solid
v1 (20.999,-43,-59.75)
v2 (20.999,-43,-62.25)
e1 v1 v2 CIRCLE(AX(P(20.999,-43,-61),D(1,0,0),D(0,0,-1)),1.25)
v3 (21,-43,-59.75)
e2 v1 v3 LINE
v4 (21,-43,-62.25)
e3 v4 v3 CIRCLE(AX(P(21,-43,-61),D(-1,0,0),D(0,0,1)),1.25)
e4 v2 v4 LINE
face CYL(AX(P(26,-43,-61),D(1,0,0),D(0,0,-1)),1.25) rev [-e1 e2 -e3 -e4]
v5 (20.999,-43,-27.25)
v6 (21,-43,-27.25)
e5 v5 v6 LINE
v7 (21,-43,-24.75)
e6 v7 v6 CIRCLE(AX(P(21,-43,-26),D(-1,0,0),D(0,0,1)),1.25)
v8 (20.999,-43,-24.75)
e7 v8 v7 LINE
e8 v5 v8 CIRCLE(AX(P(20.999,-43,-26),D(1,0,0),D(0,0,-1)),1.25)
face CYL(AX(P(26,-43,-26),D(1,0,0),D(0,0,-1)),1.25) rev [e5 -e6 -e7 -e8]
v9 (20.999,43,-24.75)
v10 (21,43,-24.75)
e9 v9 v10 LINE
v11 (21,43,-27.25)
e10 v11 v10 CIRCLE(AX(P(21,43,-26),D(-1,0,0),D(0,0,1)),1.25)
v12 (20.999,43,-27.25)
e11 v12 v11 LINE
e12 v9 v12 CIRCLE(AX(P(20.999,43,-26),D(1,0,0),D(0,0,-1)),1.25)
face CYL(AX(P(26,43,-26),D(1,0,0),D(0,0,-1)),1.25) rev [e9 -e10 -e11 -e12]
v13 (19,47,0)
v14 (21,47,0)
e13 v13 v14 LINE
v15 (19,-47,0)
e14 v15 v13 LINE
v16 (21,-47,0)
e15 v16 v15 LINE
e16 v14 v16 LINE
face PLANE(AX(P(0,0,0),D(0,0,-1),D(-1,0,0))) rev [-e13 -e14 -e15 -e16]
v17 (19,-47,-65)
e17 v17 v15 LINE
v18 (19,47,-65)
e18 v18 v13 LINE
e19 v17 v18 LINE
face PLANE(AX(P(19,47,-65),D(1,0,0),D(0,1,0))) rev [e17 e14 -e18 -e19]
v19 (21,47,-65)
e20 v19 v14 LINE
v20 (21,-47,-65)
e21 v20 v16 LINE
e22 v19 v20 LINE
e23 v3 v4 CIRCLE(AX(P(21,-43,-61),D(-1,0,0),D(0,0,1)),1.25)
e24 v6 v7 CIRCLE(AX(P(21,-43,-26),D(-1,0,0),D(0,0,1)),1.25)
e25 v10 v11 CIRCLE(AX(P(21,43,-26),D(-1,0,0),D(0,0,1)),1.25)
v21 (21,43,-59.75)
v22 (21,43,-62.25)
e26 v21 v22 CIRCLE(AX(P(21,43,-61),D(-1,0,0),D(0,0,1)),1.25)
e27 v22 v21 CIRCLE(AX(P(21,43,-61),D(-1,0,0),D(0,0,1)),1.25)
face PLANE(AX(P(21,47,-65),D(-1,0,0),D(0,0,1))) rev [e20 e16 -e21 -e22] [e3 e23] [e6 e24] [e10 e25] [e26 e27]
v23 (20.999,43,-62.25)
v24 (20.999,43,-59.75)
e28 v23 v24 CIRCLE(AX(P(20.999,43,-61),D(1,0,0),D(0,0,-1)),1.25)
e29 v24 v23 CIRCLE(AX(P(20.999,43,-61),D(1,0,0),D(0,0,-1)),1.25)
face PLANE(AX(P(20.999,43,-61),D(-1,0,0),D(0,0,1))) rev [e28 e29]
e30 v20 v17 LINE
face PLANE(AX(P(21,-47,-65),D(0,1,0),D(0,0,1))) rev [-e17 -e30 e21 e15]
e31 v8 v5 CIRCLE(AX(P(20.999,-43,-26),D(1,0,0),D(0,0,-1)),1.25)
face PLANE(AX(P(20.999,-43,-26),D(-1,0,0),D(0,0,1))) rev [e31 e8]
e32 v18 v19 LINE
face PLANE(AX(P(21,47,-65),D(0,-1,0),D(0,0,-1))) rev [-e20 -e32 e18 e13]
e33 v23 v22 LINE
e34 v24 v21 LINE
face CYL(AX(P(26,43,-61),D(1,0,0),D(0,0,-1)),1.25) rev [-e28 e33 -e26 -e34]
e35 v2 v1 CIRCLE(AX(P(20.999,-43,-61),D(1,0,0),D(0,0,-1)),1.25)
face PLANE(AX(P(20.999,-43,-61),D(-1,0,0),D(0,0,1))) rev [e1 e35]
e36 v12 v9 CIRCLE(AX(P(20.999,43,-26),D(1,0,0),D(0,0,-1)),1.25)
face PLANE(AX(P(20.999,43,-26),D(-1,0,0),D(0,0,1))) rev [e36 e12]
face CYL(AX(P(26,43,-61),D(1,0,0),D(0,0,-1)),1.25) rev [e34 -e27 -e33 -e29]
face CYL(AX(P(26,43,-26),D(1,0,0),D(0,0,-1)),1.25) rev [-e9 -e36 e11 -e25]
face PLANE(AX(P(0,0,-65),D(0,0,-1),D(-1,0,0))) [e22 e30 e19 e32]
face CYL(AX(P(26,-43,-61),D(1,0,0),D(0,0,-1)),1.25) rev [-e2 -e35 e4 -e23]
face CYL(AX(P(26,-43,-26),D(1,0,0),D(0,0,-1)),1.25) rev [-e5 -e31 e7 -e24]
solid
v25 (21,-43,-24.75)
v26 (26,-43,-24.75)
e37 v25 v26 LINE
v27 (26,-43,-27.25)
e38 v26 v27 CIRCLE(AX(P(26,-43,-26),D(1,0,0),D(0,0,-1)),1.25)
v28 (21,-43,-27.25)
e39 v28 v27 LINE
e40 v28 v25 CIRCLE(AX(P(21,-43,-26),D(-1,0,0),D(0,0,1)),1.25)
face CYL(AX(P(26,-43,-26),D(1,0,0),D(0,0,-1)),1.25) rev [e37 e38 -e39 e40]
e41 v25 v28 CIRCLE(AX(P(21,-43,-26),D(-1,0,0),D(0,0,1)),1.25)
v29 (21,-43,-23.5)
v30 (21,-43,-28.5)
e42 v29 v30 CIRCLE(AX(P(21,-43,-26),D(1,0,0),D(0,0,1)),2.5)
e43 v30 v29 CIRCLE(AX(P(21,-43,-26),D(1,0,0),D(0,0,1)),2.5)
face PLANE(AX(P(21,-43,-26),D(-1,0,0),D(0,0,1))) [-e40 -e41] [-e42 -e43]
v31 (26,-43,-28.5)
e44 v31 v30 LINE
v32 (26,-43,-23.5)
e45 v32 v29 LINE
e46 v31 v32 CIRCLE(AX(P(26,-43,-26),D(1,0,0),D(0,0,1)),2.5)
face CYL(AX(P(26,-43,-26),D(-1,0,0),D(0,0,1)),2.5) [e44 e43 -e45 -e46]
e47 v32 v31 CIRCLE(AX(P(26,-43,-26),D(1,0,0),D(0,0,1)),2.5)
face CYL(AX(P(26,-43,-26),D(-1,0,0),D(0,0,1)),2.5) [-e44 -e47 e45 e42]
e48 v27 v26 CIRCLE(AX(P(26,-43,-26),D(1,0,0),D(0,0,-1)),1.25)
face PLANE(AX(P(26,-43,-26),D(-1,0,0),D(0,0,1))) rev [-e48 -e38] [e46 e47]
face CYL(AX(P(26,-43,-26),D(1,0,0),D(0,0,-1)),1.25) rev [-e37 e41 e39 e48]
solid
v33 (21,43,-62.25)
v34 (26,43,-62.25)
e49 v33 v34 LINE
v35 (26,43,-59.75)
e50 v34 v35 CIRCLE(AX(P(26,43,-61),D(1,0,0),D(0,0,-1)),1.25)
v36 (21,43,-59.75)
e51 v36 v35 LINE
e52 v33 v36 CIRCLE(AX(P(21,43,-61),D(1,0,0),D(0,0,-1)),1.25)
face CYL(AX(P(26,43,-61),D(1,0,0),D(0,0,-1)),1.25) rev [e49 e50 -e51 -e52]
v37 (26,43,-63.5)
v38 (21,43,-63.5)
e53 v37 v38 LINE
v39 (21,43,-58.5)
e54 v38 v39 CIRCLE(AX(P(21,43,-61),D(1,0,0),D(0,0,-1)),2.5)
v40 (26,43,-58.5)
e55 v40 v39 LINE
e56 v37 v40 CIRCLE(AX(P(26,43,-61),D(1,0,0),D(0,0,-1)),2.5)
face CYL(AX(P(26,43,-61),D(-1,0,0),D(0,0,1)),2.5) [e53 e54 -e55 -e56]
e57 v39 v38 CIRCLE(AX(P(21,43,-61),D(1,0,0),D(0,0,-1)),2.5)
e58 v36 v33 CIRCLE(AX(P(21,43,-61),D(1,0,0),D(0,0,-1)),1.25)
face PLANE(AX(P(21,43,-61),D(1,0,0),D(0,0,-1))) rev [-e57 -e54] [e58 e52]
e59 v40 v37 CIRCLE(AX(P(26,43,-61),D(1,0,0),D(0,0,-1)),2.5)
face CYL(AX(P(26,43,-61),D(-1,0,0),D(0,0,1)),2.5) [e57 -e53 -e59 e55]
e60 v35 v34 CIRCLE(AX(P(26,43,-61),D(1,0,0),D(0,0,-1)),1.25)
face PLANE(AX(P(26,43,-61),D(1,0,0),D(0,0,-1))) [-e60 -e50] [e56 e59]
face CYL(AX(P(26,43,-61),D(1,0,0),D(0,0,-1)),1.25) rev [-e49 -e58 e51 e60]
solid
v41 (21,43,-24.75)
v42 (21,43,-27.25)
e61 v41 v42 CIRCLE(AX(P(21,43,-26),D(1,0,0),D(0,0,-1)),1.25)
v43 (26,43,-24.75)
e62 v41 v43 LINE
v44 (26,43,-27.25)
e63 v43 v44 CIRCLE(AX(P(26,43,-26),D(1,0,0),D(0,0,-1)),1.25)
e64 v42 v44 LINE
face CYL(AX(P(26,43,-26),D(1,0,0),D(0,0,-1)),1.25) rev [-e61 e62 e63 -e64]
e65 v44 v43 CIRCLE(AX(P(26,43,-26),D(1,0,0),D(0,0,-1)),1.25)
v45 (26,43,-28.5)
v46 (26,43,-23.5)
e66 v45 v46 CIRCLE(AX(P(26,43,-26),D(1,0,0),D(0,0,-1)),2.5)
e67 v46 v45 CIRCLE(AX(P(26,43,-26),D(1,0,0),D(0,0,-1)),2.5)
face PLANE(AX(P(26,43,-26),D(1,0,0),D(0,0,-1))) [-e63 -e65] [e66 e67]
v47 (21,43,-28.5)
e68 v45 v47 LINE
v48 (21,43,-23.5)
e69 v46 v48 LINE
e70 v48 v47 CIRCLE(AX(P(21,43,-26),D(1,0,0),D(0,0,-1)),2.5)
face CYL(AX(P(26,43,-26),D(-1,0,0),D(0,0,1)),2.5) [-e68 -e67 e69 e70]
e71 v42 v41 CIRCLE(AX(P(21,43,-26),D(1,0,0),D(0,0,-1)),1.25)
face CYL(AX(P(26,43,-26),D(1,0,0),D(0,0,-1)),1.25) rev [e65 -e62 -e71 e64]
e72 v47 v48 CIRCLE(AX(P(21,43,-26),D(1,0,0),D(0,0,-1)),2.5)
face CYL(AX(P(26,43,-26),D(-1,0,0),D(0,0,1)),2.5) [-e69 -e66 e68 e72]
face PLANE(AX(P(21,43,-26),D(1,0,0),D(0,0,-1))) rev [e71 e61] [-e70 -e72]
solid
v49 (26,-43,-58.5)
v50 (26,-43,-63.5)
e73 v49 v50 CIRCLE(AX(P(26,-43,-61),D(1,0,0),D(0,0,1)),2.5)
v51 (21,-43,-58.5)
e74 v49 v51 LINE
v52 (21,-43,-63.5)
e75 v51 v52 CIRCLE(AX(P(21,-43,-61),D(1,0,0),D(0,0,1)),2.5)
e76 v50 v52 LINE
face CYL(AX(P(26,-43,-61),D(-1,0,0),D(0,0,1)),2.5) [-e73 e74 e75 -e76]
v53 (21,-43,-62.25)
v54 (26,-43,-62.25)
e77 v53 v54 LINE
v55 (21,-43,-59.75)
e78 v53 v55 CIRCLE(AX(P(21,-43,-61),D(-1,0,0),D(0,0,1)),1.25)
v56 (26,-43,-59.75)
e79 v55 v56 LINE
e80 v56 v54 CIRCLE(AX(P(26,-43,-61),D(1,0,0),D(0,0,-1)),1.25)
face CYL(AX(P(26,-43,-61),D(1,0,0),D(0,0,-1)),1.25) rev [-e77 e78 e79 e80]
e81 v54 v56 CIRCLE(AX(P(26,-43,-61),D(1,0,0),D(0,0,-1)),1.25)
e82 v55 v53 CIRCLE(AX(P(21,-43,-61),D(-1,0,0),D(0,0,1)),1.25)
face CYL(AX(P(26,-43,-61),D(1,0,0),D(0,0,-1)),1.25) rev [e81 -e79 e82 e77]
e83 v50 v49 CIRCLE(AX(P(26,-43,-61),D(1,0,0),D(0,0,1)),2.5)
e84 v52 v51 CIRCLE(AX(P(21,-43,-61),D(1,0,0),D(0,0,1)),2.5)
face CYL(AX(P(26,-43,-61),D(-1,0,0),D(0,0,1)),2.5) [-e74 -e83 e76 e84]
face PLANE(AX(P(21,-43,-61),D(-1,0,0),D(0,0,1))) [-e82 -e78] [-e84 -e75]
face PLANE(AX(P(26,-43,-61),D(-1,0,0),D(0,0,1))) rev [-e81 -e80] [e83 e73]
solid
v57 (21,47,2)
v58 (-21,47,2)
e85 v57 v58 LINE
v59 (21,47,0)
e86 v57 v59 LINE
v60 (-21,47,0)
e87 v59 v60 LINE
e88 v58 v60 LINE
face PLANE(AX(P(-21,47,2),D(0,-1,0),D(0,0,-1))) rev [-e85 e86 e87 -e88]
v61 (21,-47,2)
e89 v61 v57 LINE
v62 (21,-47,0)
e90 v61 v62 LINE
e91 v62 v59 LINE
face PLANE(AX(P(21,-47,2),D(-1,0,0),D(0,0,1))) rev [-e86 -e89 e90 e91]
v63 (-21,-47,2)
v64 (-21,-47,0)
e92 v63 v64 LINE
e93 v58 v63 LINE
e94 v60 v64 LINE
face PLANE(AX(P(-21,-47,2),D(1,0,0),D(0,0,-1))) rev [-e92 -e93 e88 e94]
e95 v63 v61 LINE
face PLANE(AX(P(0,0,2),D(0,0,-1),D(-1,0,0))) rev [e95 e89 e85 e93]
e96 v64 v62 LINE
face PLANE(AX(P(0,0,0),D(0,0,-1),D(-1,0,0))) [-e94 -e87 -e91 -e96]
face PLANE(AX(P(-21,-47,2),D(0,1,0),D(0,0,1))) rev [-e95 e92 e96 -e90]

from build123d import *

# Parameters (mm, degrees)
SKETCH_1_W                  = 42
SKETCH_1_H                  = 94
EXTRUDE_1_DEPTH             = 2
SKETCH_2_W                  = 2
SKETCH_2_H                  = 94
EXTRUDE_2_DEPTH             = 65
SKETCH_3_R                  = 2.5
EXTRUDE_3_DEPTH             = 5
EXTRUDE_3_2_DEPTH           = 5
EXTRUDE_3_3_DEPTH           = 5
EXTRUDE_3_4_DEPTH           = 5
SKETCH_5_W                  = 1.25
SKETCH_5_H                  = 5.001
HOLE_WIZARD_M3_1_AT_2_COUNT = 2
HOLE_WIZARD_M3_1_AT_2_PITCH = 35
HOLE_WIZARD_M3_1_AT_3_COUNT = 2
HOLE_WIZARD_M3_1_AT_3_PITCH = 86
HOLE_WIZARD_M3_1_AT_4_COUNT = 2
HOLE_WIZARD_M3_1_AT_4_PITCH = 92.849340332


with BuildPart() as part:
    # 草图1 → 凸台-拉伸1 (new body)
    with BuildSketch(Plane.XY):
        Rectangle(SKETCH_1_W, SKETCH_1_H)
    extrude(amount=EXTRUDE_1_DEPTH)


with BuildPart() as body_2:
    # 草图2 → 凸台-拉伸2 (new body)
    with BuildSketch(Plane(origin=(0, 0, 0), x_dir=(-1, 0, 0), z_dir=(0, 0, -1))):
        with Locations((-20, 0)):
            Rectangle(SKETCH_2_W, SKETCH_2_H)
    extrude(amount=EXTRUDE_2_DEPTH)


with BuildPart() as body_3:
    # 草图3 → 凸台-拉伸3 (new body)
    with BuildSketch(Plane(origin=(21, 0, 0), x_dir=(0, 0, -1), z_dir=(1, 0, 0))):
        with Locations((26, 43)):
            Circle(SKETCH_3_R)
    extrude(amount=EXTRUDE_3_DEPTH)


with BuildPart() as body_4:
    # 草图3 → Extrude 3 2 (new body)
    with BuildSketch(Plane(origin=(21, 0, 0), x_dir=(0, 0, -1), z_dir=(1, 0, 0))):
        with Locations((61, 43)):
            Circle(SKETCH_3_R)
    extrude(amount=EXTRUDE_3_2_DEPTH)


with BuildPart() as body_5:
    # 草图3 → Extrude 3 3 (new body)
    with BuildSketch(Plane(origin=(21, 0, 0), x_dir=(0, 0, -1), z_dir=(1, 0, 0))):
        with Locations(Location((61, -43, 0), (0, 0, 180))):
            Circle(SKETCH_3_R)
    extrude(amount=EXTRUDE_3_3_DEPTH)


with BuildPart() as body_6:
    # 草图3 → Extrude 3 4 (new body)
    with BuildSketch(Plane(origin=(21, 0, 0), x_dir=(0, 0, -1), z_dir=(1, 0, 0))):
        with Locations(Location((26, -43, 0), (0, 0, 180))):
            Circle(SKETCH_3_R)
    extrude(amount=EXTRUDE_3_4_DEPTH)


with BuildPart() as hole_wizard_m3_1_tool:
    # 草图5 → M3 螺纹孔1 (revolve)
    with BuildSketch(Plane(origin=(26, 43, -26), x_dir=(0, 0, -1), z_dir=(0, 1, 0))):
        with Locations((0.625, 2.5005)):
            Rectangle(SKETCH_5_W, SKETCH_5_H)
    hole_wizard_m3_1 = revolve(axis=Axis((32.35, 43, -26), (-1, 0, 0)))


with BuildPart() as body_2_1:
    add(body_2.part)

    # M3 螺纹孔1: cut by hole_wizard_m3_1_tool
    add(hole_wizard_m3_1_tool.part, mode=Mode.SUBTRACT)


with BuildPart() as body_3_1:
    add(body_3.part)

    # M3 螺纹孔1: cut by hole_wizard_m3_1_tool
    add(hole_wizard_m3_1_tool.part, mode=Mode.SUBTRACT)


with BuildPart() as hole_wizard_m3_1_at_2_tool:
    # M3 螺纹孔1 at 2: M3 螺纹孔1 ×2
    with Locations(*[(0, 0, -i * HOLE_WIZARD_M3_1_AT_2_PITCH) for i in range(1, HOLE_WIZARD_M3_1_AT_2_COUNT)]):
        add(hole_wizard_m3_1)


with BuildPart() as body_2_2:
    add(body_2_1.part)

    # M3 螺纹孔1 at 2: cut by hole_wizard_m3_1_at_2_tool
    add(hole_wizard_m3_1_at_2_tool.part, mode=Mode.SUBTRACT)


with BuildPart() as body_4_1:
    add(body_4.part)

    # M3 螺纹孔1 at 2: cut by hole_wizard_m3_1_at_2_tool
    add(hole_wizard_m3_1_at_2_tool.part, mode=Mode.SUBTRACT)


with BuildPart() as hole_wizard_m3_1_at_3_tool:
    # M3 螺纹孔1 at 3: M3 螺纹孔1 ×2
    with Locations(*[(0, -i * HOLE_WIZARD_M3_1_AT_3_PITCH, 0) for i in range(1, HOLE_WIZARD_M3_1_AT_3_COUNT)]):
        add(hole_wizard_m3_1)


with BuildPart() as body_2_3:
    add(body_2_2.part)

    # M3 螺纹孔1 at 3: cut by hole_wizard_m3_1_at_3_tool
    add(hole_wizard_m3_1_at_3_tool.part, mode=Mode.SUBTRACT)


with BuildPart() as body_6_1:
    add(body_6.part)

    # M3 螺纹孔1 at 3: cut by hole_wizard_m3_1_at_3_tool
    add(hole_wizard_m3_1_at_3_tool.part, mode=Mode.SUBTRACT)


with BuildPart() as hole_wizard_m3_1_at_4_tool:
    # M3 螺纹孔1 at 4: M3 螺纹孔1 ×2
    with Locations(*[Vector(0, -0.926231674807035, -0.37695475137495615) * (i * HOLE_WIZARD_M3_1_AT_4_PITCH) for i in range(1, HOLE_WIZARD_M3_1_AT_4_COUNT)]):
        add(hole_wizard_m3_1)


with BuildPart() as body_2_4:
    add(body_2_3.part)

    # M3 螺纹孔1 at 4: cut by hole_wizard_m3_1_at_4_tool
    add(hole_wizard_m3_1_at_4_tool.part, mode=Mode.SUBTRACT)


with BuildPart() as body_5_1:
    add(body_5.part)

    # M3 螺纹孔1 at 4: cut by hole_wizard_m3_1_at_4_tool
    add(hole_wizard_m3_1_at_4_tool.part, mode=Mode.SUBTRACT)


solid = Compound([part.part, body_3_1.part, body_4_1.part, body_6_1.part, body_2_4.part, body_5_1.part])
